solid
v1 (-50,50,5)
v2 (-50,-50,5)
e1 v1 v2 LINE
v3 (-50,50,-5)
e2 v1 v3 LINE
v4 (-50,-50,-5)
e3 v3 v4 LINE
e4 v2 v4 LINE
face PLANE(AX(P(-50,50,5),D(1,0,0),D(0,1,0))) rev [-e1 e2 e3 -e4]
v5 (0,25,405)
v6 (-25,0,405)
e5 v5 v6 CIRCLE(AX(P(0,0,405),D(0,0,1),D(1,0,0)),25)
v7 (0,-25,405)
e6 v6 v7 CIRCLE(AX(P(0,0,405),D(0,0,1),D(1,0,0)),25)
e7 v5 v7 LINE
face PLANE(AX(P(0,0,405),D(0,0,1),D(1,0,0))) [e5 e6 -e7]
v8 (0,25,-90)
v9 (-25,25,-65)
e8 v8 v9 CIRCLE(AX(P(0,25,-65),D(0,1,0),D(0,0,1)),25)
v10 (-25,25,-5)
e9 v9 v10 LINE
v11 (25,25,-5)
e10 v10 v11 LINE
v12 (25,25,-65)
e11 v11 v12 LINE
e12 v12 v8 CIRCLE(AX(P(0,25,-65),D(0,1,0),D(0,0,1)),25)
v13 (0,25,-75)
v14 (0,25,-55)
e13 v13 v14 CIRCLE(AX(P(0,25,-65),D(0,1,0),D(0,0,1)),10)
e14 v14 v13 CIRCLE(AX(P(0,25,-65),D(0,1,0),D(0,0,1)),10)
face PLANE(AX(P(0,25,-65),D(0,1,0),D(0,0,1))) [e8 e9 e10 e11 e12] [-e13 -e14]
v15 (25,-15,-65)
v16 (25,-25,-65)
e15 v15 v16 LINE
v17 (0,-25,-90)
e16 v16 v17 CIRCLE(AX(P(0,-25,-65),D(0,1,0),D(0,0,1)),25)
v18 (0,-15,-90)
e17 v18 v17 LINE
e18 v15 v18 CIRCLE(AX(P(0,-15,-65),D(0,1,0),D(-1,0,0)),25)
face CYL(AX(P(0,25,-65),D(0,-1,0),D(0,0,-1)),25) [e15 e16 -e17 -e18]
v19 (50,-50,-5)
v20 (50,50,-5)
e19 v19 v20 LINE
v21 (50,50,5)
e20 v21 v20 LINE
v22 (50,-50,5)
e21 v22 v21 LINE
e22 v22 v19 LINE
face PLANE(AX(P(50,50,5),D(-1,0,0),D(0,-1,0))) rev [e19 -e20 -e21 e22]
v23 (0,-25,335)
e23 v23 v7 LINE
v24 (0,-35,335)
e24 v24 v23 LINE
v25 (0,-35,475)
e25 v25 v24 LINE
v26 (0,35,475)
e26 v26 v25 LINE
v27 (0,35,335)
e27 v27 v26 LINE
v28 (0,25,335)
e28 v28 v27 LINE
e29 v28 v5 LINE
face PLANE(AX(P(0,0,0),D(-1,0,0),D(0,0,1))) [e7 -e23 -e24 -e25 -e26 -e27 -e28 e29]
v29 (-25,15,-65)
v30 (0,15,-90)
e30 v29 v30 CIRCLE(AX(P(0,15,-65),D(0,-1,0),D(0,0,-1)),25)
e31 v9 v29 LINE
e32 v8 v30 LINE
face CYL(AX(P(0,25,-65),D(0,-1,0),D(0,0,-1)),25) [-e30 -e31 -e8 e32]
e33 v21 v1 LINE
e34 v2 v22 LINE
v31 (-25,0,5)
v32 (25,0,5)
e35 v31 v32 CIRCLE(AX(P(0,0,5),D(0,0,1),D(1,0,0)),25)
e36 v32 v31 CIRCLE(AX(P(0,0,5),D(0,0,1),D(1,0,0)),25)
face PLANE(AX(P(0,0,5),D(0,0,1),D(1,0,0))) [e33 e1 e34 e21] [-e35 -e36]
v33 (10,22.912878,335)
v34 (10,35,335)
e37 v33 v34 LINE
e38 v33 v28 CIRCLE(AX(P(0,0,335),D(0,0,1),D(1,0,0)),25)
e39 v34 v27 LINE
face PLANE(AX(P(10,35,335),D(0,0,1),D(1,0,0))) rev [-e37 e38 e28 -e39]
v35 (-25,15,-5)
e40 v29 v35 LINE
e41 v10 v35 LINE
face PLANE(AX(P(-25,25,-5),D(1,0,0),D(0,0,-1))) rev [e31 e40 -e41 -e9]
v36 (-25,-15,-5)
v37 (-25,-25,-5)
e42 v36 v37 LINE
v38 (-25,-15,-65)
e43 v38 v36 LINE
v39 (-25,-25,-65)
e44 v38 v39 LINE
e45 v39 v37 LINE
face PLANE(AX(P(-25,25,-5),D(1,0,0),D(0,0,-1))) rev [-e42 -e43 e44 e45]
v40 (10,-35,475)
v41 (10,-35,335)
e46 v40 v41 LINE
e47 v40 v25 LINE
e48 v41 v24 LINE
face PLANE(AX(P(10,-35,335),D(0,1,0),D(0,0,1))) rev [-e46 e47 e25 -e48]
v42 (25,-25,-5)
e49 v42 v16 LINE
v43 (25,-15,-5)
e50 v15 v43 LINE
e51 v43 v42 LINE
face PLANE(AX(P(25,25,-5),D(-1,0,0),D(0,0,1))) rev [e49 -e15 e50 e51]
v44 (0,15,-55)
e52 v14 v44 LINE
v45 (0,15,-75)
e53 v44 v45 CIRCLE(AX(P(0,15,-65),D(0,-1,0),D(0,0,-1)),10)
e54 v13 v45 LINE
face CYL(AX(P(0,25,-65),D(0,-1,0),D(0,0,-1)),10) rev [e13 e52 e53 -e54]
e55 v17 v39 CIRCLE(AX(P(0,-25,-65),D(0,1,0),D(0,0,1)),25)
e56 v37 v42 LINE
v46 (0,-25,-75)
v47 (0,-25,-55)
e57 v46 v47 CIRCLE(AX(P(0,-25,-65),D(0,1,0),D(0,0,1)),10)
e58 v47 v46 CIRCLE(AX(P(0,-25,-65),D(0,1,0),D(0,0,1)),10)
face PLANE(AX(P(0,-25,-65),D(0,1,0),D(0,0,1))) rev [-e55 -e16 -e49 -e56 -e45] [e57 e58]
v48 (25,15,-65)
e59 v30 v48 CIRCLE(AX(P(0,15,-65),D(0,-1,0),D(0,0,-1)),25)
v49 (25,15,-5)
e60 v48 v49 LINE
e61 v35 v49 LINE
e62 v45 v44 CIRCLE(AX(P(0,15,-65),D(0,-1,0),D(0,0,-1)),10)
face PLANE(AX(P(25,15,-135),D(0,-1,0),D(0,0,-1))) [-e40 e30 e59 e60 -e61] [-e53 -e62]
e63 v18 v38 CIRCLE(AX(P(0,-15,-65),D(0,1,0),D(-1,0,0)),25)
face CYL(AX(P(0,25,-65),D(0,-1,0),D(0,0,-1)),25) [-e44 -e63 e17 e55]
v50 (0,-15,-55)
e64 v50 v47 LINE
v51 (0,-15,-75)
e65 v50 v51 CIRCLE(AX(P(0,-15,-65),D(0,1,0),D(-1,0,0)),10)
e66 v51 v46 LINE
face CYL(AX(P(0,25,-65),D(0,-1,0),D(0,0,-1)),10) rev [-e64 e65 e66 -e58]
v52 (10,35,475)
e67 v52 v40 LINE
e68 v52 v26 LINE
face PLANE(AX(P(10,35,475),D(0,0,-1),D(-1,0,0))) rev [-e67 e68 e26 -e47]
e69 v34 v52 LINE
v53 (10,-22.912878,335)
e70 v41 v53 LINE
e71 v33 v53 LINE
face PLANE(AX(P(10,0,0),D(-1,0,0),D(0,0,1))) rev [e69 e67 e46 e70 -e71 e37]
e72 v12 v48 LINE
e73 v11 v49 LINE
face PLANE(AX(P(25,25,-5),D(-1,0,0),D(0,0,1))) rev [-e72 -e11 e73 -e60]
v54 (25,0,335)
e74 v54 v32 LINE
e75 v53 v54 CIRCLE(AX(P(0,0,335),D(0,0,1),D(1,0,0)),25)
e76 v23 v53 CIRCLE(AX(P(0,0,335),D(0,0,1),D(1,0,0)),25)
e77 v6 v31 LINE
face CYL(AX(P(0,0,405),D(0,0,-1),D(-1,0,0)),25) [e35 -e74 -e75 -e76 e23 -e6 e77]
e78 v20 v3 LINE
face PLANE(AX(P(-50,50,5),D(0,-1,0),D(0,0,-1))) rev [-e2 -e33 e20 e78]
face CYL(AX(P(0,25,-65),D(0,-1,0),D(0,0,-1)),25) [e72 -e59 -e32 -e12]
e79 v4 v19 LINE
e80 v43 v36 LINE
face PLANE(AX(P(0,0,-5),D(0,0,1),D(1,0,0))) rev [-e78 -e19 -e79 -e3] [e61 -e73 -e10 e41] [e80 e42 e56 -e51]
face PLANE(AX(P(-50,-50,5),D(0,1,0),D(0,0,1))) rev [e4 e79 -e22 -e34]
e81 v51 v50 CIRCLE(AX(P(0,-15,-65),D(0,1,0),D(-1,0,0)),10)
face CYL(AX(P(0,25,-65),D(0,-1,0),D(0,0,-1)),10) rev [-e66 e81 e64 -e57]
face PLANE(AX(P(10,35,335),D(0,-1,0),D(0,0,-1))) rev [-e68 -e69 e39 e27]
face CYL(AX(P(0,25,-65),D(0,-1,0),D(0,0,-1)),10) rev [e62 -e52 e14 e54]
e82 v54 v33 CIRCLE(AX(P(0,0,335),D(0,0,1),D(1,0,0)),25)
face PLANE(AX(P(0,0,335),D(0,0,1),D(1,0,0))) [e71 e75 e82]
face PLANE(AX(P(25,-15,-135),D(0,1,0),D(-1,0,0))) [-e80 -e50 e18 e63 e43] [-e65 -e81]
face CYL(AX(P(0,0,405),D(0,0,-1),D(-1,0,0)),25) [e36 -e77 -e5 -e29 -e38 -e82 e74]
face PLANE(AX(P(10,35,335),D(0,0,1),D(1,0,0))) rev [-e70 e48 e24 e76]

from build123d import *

# Parameters (mm, degrees)
SKETCH1_W           = 100
SKETCH1_H           = 100
BOSS_EXTRUDE1_DEPTH = 5
SKETCH2_R           = 10
BOSS_EXTRUDE2_DEPTH = 25
SKETCH3_W           = 50
SKETCH3_H           = 30
CUT_EXTRUDE1_DEPTH  = 130
SKETCH4_R           = 25
BOSS_EXTRUDE3_DEPTH = 400
CUT_EXTRUDE2_START  = -70
CUT_EXTRUDE2_DEPTH  = 70
SKETCH7_W           = 140
SKETCH7_H           = 70
BOSS_EXTRUDE4_DEPTH = 10


with BuildPart() as part:
    # Sketch1 → Boss-Extrude1 (new, symmetric)
    with BuildSketch(Plane.XY):
        Rectangle(SKETCH1_W, SKETCH1_H)
    extrude(amount=BOSS_EXTRUDE1_DEPTH, both=True)

    # Sketch2 → Boss-Extrude2 (add, symmetric)
    with BuildSketch(Plane(origin=(0, 0, 0), x_dir=(1, 0, 0), z_dir=(0, 1, 0))):
        with BuildLine():
            Line((-25, 5), (25, 5))
            Line((25, 5), (25, 65))
            ThreePointArc((25, 65), (0, 90), (-25, 65))
            Line((-25, 65), (-25, 5))
        make_face()
        with Locations(Location((0, 65, 0), (0, 0, 270))):
            Circle(SKETCH2_R, mode=Mode.SUBTRACT)
    extrude(amount=BOSS_EXTRUDE2_DEPTH, both=True)

    # Sketch3 → Cut-Extrude1 (cut)
    with BuildSketch(Plane(origin=(0, 0, -5), x_dir=(-1, 0, 0), z_dir=(0, 0, -1))):
        Rectangle(SKETCH3_W, SKETCH3_H)
    extrude(amount=CUT_EXTRUDE1_DEPTH, mode=Mode.SUBTRACT)

    # Sketch4 → Boss-Extrude3 (add)
    with BuildSketch(Plane.XY.offset(5)):
        with Locations(Location((0, 0, 0), (0, 0, 180))):
            Circle(SKETCH4_R)
    extrude(amount=BOSS_EXTRUDE3_DEPTH)

    # Sketch5 → Cut-Extrude2 (cut)
    with BuildSketch(Plane.XY.offset(405).offset(CUT_EXTRUDE2_START)):
        with BuildLine():
            Line((0, 25), (0, -25))
            ThreePointArc((0, -25), (25, 0), (0, 25))
        make_face()
    extrude(amount=CUT_EXTRUDE2_DEPTH, mode=Mode.SUBTRACT)

    # Sketch7 → Boss-Extrude4 (add)
    with BuildSketch(Plane(origin=(0, 0, 0), x_dir=(0, 0, -1), z_dir=(1, 0, 0))):
        with Locations((-405, 0)):
            Rectangle(SKETCH7_W, SKETCH7_H)
    extrude(amount=BOSS_EXTRUDE4_DEPTH)


solid = part.part
